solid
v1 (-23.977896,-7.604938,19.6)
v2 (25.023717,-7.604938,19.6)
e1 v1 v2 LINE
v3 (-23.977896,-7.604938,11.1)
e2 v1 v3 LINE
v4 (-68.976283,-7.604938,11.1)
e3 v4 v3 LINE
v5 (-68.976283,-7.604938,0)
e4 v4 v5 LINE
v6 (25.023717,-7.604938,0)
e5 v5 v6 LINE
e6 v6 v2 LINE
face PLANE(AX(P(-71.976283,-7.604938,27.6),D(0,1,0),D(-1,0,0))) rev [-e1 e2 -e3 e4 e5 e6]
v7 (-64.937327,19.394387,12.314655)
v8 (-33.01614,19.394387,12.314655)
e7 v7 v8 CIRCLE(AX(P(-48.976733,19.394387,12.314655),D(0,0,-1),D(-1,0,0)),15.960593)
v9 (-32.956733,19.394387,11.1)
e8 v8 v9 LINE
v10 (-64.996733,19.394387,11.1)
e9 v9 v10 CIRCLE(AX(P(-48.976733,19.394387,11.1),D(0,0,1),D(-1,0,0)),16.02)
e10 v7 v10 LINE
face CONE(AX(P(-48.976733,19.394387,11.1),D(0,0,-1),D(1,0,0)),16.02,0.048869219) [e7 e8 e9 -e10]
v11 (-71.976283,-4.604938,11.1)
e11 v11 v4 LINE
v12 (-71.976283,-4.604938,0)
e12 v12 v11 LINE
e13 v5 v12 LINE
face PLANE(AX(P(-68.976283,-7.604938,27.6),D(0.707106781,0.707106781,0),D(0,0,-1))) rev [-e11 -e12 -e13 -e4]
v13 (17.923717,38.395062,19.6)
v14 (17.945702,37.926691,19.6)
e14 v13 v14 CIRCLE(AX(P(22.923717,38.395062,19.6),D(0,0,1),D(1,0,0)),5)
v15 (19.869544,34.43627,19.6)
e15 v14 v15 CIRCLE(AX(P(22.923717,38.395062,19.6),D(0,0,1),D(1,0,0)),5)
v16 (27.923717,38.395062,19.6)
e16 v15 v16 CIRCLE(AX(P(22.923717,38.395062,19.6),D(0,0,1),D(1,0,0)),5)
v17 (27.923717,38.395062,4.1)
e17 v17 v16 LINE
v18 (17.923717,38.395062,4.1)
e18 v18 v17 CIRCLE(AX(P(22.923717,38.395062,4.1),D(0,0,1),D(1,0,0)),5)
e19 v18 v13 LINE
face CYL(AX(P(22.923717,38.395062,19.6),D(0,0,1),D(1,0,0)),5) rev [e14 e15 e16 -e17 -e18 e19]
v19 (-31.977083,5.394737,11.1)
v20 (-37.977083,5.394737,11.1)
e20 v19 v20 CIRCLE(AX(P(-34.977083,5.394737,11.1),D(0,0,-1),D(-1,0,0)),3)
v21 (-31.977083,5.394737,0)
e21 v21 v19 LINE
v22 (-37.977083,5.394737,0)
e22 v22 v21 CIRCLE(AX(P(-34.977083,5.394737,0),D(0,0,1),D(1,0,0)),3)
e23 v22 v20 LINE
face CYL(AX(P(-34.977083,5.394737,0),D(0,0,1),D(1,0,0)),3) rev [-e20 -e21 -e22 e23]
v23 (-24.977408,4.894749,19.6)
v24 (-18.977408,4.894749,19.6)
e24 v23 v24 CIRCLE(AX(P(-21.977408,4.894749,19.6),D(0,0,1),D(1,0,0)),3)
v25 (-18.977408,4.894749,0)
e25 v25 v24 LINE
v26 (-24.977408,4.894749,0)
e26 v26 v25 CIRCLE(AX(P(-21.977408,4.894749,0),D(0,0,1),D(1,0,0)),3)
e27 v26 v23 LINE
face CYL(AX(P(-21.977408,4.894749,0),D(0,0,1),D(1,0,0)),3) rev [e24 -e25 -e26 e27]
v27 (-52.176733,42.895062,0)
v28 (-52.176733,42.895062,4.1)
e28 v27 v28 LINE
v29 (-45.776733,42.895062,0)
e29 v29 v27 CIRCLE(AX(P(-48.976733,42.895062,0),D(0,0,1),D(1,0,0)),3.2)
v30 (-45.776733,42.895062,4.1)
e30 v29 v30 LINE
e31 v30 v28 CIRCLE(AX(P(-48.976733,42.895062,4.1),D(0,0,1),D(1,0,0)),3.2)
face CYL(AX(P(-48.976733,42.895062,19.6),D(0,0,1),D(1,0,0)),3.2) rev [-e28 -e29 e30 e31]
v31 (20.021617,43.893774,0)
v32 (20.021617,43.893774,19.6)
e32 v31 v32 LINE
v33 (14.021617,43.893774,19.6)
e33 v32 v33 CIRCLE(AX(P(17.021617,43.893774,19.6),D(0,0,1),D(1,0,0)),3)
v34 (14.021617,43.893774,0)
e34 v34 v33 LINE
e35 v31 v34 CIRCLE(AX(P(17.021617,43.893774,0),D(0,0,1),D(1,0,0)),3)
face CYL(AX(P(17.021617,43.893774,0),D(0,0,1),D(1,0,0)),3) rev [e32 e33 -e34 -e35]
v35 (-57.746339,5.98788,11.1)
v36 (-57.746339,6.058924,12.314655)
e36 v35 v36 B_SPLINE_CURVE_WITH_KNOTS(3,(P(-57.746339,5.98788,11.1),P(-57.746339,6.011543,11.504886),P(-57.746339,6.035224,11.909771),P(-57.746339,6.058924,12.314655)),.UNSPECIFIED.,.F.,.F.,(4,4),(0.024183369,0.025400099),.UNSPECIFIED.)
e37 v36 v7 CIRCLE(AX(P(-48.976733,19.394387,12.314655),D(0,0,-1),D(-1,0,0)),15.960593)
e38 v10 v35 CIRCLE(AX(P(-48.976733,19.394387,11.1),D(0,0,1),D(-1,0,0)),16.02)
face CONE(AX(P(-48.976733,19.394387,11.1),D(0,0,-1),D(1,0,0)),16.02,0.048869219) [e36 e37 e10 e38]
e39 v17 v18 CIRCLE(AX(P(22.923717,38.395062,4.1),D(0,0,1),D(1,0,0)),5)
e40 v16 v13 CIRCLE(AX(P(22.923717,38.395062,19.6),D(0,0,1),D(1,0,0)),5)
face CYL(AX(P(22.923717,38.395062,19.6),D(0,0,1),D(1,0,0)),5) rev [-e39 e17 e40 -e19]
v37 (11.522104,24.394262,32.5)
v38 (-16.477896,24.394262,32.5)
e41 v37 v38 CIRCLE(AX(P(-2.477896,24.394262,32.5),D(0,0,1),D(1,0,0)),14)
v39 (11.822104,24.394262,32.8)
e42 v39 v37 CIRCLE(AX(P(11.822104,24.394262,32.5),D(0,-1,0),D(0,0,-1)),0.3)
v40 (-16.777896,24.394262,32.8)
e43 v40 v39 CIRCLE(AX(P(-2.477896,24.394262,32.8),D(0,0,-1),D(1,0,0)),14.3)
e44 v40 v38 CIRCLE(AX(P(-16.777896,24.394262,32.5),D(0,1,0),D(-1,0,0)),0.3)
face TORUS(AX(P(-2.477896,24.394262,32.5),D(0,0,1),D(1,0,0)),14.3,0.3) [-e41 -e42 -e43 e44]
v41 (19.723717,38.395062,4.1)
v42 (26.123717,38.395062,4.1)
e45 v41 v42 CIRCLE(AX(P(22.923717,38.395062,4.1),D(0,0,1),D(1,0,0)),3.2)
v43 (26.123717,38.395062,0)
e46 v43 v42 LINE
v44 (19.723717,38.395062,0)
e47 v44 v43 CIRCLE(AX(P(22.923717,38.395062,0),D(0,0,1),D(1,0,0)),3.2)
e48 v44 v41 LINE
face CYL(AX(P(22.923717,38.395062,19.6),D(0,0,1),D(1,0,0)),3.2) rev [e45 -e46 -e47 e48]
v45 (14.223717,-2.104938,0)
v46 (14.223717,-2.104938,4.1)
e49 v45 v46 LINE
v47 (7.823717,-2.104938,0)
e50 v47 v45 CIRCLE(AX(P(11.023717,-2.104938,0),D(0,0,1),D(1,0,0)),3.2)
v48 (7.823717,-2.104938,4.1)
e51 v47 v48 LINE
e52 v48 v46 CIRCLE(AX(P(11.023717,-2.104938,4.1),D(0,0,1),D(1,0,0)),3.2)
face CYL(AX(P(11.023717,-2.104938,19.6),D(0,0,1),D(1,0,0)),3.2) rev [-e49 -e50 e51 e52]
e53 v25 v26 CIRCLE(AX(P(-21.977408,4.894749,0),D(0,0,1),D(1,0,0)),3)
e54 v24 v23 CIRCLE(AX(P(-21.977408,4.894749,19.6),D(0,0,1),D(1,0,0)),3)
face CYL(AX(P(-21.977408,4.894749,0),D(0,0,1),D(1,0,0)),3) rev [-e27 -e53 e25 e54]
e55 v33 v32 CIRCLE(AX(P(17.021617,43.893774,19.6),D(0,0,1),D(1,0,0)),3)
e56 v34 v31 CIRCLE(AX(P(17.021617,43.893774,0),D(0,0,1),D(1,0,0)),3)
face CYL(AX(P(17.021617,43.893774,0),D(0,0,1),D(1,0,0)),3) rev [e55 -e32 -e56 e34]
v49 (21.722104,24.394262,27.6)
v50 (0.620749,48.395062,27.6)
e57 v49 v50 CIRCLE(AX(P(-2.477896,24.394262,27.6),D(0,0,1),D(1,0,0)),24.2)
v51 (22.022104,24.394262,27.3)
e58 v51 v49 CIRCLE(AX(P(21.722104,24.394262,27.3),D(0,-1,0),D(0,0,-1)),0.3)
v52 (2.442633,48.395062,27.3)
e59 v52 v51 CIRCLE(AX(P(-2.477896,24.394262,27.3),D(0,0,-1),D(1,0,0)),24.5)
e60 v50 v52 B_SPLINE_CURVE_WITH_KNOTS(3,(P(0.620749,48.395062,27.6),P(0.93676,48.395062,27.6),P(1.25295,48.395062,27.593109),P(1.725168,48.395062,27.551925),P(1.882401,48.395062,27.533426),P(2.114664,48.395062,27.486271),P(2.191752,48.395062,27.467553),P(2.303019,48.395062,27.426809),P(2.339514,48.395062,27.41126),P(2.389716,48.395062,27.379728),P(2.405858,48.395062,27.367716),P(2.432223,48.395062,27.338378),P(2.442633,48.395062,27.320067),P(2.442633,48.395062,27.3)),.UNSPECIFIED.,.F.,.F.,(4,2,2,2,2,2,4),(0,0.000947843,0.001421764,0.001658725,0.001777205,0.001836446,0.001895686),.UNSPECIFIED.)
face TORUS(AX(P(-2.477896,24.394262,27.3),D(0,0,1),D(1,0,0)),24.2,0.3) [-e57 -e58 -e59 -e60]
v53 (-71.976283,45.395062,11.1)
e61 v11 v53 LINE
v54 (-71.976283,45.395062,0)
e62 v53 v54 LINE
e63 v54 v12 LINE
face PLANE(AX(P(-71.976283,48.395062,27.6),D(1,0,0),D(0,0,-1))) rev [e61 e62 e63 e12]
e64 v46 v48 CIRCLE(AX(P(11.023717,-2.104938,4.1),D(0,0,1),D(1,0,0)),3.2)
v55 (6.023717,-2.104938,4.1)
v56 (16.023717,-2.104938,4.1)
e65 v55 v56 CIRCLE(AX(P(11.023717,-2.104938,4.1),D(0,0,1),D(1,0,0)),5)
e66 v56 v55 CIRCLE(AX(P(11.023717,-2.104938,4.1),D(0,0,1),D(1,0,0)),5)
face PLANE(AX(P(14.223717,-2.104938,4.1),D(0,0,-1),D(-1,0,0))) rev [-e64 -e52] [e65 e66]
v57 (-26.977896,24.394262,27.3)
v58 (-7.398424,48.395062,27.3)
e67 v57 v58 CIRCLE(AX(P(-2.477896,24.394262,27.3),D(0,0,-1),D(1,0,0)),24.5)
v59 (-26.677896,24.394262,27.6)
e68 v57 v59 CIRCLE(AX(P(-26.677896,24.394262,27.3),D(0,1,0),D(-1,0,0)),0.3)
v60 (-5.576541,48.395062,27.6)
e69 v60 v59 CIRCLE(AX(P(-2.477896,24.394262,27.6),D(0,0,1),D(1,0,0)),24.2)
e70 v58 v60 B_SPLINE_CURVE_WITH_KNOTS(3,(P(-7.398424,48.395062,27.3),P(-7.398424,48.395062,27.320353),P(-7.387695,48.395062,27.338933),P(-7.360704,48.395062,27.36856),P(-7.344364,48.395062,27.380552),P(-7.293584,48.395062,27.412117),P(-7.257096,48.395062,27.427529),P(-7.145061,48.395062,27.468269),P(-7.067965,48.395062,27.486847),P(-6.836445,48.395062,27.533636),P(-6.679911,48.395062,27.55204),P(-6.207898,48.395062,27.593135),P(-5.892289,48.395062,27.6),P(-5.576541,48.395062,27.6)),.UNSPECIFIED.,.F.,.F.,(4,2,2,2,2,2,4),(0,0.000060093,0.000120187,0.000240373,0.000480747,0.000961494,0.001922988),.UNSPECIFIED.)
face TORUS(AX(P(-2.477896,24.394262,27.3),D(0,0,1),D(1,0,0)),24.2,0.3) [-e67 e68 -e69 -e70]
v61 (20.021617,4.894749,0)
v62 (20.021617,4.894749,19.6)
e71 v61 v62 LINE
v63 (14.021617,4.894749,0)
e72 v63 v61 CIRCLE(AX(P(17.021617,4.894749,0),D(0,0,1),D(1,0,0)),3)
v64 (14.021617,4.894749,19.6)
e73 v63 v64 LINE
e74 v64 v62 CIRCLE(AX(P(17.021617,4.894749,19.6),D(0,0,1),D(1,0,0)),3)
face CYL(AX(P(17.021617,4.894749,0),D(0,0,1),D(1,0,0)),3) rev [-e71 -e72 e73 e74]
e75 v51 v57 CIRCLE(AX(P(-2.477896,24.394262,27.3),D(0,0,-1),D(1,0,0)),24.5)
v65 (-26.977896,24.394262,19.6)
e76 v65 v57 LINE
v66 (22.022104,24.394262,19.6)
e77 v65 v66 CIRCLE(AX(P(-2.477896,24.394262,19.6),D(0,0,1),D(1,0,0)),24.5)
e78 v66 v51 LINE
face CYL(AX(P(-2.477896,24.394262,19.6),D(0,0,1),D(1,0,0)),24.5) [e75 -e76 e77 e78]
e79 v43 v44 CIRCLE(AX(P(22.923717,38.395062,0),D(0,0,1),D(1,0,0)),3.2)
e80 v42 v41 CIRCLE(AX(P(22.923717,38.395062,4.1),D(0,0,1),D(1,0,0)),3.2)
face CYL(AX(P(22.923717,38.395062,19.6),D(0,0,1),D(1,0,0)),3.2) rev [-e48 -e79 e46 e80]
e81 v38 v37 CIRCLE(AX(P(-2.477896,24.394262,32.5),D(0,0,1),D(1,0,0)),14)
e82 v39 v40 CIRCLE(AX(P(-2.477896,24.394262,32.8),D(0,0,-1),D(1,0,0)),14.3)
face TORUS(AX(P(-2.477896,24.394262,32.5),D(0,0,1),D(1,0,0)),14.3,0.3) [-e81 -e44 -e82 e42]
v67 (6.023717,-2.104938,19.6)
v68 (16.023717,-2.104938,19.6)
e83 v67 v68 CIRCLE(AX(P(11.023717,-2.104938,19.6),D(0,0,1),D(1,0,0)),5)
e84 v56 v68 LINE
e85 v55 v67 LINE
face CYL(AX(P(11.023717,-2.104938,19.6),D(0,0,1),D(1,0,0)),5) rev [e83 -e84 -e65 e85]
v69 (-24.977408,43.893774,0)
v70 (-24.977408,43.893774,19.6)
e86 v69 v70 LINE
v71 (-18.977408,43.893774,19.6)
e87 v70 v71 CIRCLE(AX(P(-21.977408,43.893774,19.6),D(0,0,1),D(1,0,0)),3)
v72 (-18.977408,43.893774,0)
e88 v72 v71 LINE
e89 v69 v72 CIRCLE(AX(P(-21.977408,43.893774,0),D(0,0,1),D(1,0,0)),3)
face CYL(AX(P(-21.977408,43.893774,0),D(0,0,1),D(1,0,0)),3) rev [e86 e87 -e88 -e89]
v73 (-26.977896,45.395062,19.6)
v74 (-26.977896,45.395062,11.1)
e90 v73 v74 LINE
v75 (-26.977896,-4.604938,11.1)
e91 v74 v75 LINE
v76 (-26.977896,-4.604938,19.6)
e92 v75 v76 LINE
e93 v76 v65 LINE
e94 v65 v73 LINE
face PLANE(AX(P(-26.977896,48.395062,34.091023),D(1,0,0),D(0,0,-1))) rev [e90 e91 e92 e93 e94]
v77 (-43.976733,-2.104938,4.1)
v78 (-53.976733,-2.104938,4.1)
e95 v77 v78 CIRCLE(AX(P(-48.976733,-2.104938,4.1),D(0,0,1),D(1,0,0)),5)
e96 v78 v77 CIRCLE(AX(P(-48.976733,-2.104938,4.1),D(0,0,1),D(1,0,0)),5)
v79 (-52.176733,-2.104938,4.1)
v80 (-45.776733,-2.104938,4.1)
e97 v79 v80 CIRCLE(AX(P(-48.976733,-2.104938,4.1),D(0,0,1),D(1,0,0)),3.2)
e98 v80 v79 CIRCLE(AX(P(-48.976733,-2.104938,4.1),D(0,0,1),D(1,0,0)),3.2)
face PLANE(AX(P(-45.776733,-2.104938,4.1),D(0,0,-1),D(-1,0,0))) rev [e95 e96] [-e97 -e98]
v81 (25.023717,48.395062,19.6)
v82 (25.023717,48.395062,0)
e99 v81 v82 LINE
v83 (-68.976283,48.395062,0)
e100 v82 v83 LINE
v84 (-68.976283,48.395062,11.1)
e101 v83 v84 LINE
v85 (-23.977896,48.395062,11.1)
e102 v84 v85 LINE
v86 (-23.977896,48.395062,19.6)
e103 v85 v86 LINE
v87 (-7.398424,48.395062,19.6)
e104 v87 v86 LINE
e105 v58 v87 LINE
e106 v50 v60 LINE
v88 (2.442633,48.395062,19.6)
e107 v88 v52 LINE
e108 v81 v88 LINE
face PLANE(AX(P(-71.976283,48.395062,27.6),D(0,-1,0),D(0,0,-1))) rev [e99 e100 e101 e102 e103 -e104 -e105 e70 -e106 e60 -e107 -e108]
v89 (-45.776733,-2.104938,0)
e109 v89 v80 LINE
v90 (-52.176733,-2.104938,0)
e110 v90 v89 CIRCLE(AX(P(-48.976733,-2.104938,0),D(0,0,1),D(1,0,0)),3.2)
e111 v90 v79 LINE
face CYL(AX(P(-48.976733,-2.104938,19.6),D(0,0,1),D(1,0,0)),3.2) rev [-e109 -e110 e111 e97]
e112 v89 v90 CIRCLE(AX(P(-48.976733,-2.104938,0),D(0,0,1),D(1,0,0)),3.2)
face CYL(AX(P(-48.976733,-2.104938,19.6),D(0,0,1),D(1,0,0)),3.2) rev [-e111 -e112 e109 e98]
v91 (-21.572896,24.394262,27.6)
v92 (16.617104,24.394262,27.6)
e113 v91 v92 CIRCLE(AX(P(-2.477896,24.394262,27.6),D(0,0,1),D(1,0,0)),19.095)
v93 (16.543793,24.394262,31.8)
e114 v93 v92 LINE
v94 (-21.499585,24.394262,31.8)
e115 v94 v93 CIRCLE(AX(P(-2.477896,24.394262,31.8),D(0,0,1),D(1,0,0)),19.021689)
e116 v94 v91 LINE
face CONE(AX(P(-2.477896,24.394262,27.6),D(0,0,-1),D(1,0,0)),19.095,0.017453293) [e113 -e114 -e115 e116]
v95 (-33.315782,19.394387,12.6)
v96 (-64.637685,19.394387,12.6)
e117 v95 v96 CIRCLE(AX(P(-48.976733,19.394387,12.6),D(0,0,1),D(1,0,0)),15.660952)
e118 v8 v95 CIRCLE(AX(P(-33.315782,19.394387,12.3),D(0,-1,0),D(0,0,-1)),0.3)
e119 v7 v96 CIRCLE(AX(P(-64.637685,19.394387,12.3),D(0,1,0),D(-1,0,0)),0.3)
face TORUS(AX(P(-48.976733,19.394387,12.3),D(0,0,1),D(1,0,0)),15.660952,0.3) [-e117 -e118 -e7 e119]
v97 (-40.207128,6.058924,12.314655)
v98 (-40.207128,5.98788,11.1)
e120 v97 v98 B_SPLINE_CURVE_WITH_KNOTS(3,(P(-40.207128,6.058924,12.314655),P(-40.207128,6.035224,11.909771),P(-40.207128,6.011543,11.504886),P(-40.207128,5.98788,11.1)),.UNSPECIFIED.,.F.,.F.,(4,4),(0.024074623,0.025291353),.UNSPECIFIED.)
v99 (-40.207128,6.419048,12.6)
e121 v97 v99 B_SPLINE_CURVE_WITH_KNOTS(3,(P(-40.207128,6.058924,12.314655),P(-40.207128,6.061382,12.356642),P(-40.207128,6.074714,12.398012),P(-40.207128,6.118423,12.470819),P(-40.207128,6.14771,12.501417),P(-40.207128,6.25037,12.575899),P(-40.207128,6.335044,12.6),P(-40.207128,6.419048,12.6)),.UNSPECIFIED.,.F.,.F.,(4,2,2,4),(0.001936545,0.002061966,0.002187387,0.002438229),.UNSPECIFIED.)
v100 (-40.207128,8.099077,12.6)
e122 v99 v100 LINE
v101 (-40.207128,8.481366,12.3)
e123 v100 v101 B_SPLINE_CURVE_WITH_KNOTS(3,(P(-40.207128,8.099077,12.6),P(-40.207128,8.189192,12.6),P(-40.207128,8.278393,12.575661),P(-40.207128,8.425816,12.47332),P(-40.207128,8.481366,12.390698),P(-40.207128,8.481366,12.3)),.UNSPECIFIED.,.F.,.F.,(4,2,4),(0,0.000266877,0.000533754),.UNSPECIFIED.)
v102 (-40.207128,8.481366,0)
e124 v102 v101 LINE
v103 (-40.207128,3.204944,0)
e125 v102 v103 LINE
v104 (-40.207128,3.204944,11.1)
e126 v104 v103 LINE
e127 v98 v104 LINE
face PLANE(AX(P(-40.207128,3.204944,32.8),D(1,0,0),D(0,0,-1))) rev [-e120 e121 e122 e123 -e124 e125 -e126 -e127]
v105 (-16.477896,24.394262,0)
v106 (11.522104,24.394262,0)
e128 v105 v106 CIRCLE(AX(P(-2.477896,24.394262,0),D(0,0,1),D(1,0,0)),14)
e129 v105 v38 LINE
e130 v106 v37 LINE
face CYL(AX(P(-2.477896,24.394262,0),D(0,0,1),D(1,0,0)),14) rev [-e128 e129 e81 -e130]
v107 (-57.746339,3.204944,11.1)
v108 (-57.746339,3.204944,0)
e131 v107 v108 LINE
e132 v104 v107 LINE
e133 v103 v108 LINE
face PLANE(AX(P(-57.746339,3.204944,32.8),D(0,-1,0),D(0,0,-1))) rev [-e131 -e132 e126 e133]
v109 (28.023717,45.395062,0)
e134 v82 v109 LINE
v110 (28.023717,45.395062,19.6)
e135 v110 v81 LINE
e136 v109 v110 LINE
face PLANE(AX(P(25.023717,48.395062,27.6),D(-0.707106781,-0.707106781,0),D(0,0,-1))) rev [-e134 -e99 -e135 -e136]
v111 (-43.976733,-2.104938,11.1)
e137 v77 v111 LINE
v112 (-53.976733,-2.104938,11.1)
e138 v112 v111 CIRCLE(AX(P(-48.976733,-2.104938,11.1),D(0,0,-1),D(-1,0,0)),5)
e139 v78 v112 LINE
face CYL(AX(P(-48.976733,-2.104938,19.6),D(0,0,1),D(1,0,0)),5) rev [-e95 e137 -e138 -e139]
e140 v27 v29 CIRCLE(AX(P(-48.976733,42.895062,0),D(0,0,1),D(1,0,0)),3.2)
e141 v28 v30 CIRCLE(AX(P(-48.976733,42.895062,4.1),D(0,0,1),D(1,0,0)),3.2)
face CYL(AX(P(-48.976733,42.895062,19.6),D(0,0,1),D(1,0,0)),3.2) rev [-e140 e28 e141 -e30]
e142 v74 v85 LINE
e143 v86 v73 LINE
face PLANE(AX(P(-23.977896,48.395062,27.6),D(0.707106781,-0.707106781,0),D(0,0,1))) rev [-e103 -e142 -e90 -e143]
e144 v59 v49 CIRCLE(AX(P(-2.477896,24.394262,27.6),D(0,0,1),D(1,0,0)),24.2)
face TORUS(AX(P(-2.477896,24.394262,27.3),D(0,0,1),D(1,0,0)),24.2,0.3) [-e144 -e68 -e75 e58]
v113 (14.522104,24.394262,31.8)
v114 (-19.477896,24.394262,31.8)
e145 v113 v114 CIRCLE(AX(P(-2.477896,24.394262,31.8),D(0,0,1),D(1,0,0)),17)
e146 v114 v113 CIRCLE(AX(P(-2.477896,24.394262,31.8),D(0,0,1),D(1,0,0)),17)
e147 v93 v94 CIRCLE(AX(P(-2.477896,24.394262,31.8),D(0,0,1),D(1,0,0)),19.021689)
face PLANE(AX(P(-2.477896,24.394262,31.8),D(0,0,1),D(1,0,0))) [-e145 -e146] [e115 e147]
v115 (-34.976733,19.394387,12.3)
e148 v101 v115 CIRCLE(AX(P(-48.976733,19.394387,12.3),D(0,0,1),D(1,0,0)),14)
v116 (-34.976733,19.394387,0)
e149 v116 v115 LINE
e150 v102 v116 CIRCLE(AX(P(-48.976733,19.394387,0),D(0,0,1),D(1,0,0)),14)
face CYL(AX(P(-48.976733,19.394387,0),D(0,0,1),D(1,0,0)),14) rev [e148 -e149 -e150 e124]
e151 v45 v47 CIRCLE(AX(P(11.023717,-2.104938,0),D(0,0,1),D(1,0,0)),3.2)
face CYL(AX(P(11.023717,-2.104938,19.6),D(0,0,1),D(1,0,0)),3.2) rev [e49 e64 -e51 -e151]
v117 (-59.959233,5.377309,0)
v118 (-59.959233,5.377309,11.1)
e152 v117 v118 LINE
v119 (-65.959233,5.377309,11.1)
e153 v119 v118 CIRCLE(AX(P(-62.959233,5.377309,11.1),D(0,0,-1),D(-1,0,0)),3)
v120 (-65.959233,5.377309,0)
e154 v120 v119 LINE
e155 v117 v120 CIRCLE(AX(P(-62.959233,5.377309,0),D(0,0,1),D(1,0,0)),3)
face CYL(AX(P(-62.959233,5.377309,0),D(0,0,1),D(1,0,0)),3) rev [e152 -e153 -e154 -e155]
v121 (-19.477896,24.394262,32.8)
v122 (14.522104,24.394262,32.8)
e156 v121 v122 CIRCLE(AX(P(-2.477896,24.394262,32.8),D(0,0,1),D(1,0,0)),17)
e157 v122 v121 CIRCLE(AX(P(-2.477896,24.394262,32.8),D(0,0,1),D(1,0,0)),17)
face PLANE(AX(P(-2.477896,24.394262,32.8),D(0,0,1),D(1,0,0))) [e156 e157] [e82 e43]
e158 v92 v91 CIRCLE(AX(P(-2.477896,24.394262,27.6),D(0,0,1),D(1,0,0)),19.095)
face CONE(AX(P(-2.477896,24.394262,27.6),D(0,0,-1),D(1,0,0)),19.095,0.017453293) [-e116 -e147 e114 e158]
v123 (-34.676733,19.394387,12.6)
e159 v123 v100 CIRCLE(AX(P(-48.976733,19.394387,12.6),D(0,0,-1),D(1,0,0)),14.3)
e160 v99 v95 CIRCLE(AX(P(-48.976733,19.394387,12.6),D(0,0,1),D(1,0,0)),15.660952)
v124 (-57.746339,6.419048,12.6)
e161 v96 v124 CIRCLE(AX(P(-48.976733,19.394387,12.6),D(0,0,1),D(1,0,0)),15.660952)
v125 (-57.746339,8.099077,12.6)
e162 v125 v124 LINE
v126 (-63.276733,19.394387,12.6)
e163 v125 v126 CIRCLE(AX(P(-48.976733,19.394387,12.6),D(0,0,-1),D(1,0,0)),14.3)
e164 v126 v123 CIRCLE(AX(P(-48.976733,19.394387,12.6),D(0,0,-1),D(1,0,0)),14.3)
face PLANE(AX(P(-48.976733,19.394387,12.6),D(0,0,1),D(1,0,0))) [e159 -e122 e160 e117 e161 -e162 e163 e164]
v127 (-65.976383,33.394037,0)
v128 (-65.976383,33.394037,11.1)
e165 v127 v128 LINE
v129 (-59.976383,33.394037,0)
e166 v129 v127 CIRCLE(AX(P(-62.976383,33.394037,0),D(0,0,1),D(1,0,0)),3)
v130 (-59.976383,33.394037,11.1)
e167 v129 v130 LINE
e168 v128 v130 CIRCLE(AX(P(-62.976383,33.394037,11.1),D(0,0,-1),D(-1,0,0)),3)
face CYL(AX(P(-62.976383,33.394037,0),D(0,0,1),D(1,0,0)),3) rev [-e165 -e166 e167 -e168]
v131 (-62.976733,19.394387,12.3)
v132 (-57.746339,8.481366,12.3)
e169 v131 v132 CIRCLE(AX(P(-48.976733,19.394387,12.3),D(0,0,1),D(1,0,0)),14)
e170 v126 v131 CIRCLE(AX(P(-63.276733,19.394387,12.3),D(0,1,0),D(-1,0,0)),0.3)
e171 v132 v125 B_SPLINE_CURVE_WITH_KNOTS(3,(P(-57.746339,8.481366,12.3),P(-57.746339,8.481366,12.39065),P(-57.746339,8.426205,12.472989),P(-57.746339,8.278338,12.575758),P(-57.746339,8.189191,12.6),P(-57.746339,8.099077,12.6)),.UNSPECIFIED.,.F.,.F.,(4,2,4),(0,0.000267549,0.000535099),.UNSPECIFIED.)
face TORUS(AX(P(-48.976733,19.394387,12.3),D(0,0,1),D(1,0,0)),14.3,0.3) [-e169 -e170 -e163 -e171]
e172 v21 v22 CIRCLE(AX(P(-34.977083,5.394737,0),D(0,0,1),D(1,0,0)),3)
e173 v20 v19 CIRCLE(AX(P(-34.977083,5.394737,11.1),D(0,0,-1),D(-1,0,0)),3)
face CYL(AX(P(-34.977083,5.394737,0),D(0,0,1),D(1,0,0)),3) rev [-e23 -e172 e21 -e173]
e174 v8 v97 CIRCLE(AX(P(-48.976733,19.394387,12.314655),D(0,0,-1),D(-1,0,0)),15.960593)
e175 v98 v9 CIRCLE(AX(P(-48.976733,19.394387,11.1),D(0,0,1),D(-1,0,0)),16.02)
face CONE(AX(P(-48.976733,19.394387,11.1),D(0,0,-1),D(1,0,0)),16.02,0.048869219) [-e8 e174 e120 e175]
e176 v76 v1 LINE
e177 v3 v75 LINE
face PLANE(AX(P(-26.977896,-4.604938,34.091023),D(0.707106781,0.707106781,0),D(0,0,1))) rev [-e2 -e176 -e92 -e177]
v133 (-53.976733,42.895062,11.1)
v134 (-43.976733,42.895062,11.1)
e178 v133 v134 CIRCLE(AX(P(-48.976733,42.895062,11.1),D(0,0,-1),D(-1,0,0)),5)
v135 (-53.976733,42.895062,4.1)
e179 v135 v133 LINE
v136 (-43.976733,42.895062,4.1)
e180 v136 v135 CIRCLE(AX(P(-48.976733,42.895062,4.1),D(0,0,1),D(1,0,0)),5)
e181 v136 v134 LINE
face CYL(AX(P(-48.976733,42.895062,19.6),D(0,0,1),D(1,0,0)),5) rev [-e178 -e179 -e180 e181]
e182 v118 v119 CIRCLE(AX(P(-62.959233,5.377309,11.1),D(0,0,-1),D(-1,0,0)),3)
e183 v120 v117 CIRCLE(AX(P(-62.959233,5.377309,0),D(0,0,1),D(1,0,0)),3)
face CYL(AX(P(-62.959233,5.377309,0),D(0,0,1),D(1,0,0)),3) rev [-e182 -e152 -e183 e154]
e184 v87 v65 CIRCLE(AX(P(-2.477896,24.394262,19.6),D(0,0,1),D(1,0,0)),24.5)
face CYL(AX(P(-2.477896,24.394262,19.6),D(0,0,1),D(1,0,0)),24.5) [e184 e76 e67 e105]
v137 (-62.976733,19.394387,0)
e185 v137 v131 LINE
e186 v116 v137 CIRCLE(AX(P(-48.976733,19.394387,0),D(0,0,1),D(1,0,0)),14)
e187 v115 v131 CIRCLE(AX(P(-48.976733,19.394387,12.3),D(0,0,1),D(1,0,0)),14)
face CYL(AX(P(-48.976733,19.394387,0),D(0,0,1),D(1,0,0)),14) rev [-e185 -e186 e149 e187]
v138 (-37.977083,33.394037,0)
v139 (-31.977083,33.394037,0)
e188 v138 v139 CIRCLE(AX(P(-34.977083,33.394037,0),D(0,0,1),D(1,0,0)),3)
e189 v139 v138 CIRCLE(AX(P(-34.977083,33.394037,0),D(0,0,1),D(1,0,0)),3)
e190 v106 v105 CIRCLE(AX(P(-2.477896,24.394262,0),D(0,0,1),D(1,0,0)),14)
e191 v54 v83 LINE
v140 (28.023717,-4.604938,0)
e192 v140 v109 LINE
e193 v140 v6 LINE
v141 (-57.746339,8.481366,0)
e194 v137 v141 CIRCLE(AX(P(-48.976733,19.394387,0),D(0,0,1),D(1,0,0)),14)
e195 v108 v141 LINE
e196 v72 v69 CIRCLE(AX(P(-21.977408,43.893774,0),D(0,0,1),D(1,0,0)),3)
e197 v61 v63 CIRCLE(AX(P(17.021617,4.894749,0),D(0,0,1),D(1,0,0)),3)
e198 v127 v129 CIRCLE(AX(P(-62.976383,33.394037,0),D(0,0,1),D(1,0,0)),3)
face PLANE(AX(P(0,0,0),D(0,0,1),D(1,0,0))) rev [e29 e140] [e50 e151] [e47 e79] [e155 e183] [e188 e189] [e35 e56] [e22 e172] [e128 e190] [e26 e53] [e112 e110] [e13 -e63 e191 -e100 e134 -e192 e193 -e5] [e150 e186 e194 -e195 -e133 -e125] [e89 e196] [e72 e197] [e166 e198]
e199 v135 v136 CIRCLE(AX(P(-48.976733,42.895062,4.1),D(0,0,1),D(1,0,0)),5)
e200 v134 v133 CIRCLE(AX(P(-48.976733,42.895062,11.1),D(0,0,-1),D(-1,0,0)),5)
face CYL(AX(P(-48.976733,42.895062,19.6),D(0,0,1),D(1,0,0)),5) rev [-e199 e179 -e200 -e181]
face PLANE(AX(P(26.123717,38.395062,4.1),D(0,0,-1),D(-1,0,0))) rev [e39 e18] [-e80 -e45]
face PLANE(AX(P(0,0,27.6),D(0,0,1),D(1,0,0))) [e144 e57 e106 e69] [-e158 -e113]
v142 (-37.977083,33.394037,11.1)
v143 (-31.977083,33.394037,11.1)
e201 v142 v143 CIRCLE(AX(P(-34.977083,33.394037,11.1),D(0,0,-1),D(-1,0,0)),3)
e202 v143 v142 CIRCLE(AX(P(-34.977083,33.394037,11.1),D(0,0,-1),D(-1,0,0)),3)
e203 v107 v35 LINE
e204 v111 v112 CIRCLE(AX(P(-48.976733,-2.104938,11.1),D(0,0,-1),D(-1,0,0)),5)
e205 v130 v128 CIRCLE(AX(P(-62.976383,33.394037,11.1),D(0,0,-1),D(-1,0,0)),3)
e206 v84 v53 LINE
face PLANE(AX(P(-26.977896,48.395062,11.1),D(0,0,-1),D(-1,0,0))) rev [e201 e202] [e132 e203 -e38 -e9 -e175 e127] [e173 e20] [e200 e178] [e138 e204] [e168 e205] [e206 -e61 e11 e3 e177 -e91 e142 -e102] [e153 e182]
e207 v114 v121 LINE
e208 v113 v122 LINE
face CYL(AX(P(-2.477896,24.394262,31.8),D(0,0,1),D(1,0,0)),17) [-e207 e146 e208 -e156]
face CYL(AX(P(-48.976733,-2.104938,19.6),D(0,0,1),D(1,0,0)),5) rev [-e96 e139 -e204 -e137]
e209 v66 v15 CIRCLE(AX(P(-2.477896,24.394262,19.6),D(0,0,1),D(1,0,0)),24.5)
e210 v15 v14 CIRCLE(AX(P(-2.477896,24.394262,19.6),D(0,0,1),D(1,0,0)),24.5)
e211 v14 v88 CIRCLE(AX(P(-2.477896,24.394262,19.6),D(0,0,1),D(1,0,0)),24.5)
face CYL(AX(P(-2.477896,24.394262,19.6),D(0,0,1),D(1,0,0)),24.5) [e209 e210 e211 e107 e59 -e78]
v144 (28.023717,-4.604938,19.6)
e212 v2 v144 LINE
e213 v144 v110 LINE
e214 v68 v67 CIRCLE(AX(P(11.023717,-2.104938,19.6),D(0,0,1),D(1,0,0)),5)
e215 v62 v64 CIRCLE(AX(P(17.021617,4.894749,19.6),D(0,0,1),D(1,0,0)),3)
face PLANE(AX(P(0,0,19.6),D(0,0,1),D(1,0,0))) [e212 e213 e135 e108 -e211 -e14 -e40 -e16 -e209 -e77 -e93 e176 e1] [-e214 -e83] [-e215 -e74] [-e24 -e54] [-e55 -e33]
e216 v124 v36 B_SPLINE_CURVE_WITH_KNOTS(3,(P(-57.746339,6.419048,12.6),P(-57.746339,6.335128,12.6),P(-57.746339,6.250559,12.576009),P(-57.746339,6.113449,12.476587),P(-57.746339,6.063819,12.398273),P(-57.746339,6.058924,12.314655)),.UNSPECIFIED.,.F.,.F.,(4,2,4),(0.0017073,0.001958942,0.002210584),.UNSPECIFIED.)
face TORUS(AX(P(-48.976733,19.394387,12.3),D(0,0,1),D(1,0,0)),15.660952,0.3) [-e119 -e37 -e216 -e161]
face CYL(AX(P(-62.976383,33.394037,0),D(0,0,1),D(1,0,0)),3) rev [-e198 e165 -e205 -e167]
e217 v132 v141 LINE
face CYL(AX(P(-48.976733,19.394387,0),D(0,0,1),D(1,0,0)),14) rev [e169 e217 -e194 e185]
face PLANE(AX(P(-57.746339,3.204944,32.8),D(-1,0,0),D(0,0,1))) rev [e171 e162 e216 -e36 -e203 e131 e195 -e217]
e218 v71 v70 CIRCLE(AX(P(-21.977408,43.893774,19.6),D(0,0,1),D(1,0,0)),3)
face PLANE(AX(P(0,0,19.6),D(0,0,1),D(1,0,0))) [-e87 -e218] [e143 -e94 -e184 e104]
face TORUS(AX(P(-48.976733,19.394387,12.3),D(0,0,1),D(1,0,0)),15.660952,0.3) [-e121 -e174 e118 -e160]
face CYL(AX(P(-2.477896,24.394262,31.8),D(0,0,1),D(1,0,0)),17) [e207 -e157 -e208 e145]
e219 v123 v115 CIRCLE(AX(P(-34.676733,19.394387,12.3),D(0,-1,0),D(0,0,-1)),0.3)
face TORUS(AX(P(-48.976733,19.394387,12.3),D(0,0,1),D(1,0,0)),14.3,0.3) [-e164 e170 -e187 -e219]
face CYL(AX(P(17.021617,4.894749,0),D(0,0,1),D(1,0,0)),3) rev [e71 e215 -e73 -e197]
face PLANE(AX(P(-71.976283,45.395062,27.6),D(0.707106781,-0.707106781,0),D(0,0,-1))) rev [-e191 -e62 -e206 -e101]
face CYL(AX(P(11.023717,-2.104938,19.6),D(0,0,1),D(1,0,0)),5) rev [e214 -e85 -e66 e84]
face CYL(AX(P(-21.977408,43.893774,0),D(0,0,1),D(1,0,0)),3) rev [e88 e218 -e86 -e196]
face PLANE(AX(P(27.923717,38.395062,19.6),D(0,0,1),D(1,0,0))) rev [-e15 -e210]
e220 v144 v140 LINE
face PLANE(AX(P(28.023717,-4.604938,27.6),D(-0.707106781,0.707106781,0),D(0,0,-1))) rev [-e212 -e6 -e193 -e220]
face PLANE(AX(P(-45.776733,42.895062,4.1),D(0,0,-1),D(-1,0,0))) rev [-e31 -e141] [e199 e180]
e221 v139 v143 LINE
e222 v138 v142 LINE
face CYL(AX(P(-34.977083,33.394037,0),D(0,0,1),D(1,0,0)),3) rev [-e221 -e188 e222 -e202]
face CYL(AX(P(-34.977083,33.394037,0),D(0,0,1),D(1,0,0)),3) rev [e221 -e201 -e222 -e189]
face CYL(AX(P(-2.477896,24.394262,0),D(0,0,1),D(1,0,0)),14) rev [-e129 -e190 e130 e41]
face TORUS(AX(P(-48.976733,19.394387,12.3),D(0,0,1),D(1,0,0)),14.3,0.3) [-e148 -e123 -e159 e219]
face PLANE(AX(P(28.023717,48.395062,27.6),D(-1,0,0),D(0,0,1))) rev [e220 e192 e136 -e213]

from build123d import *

# Parameters (mm, degrees)
SKETCH1_W                                    = 100
SKETCH1_H                                    = 56
BOSS_EXTRUDE1_DEPTH                          = 27.6
SKETCH2_R                                    = 19.095
BOSS_EXTRUDE2_DEPTH                          = 5.2
BOSS_EXTRUDE2_TAPER                          = 1
SKETCH4_W                                    = 117.356631531
SKETCH4_H                                    = 93.478875332
SKETCH4_R                                    = 24.5
CUT_EXTRUDE1_DEPTH                           = 8
FILLET1_R                                    = 0.3
SKETCH5_W                                    = 56.36290192
SKETCH5_H                                    = 22.991022885
CUT_EXTRUDE2_DEPTH                           = 97.914526075
SKETCH6_R                                    = 16.02
BOSS_EXTRUDE3_DEPTH                          = 1.5
BOSS_EXTRUDE3_TAPER                          = 2.8
FILLET2_R                                    = 0.3
CUT_EXTRUDE3_DEPTH                           = 90.406696404
CUT_EXTRUDE3_DEPTH_BACK                      = 90.406696404
SKETCH7_R                                    = 3
SKETCH8_R                                    = 14
CUT_EXTRUDE4_DEPTH                           = 90.054519041
SKETCH9_W                                    = 17.539210826
SKETCH9_H                                    = 13.762480841
CUT_EXTRUDE5_DEPTH                           = 93.728136852
CHAMFER1_SIZE                                = 3
CBORE_FOR_M6_HEX_SOCKET_HEAD_CAP_SCR_2_COUNT = 2
CBORE_FOR_M6_HEX_SOCKET_HEAD_CAP_SCR_2_PITCH = 75.00036
CBORE_FOR_M6_HEX_SOCKET_HEAD_CAP_SCR_3_COUNT = 2
CBORE_FOR_M6_HEX_SOCKET_HEAD_CAP_SCR_3_PITCH = 45
CBORE_FOR_M6_HEX_SOCKET_HEAD_CAP_SCR_4_COUNT = 2
CBORE_FOR_M6_HEX_SOCKET_HEAD_CAP_SCR_4_PITCH = 72.041132072
SKETCH12_R                                   = 14
CUT_EXTRUDE6_DEPTH                           = 93.728136852
FILLET3_R                                    = 0.3
SKETCH13_R                                   = 21.226121865
SKETCH13_R_2                                 = 17
CUT_EXTRUDE7_DEPTH                           = 1


with BuildPart() as part:
    # Sketch1 → Boss-Extrude1 (new body)
    with BuildSketch(Plane.XY):
        with Locations((-21.976283301, 20.395061728)):
            Rectangle(SKETCH1_W, SKETCH1_H)
    extrude(amount=BOSS_EXTRUDE1_DEPTH)

    # Sketch2 → Boss-Extrude2 (add)
    with BuildSketch(Plane.XY.offset(27.6)):
        with Locations((-2.477895801, 24.394261729)):
            Circle(SKETCH2_R)
    extrude(amount=BOSS_EXTRUDE2_DEPTH, taper=BOSS_EXTRUDE2_TAPER)

    # Sketch4 → Cut-Extrude1 (cut)
    with BuildSketch(Plane.XY.offset(27.6)):
        with Locations((-19.266750683, 19.548332785)):
            Rectangle(SKETCH4_W, SKETCH4_H)
        with Locations((-2.477895801, 24.394261729)):
            Circle(SKETCH4_R, mode=Mode.SUBTRACT)
    extrude(amount=-CUT_EXTRUDE1_DEPTH, mode=Mode.SUBTRACT)

    # Fillet1
    fillet1_edges = [part.edges().sort_by_distance(p)[0] for p in [
        (-21.482129463, 24.394261729, 32.8),
    ]]
    fillet(fillet1_edges, radius=FILLET1_R)

    # Sketch5 → Cut-Extrude2 (cut, through all)
    with BuildSketch(Plane.XZ.offset(7.604938272)):
        with Locations((-55.159346761, 22.595511443)):
            Rectangle(SKETCH5_W, SKETCH5_H)
    extrude(amount=-CUT_EXTRUDE2_DEPTH, mode=Mode.SUBTRACT)

    # Sketch6 → Boss-Extrude3 (add)
    with BuildSketch(Plane.XY.offset(11.1)):
        with Locations((-48.976733301, 19.394386728)):
            Circle(SKETCH6_R)
    extrude(amount=BOSS_EXTRUDE3_DEPTH, taper=BOSS_EXTRUDE3_TAPER)

    # Fillet2
    fillet2_edges = [part.edges().sort_by_distance(p)[0] for p in [
        (-64.923371062, 19.394386728, 12.6),
    ]]
    fillet(fillet2_edges, radius=FILLET2_R)

    # Sketch7 → Cut-Extrude3 (cut, two sides: drawn at the far end of the back side and taken through both)
    with BuildSketch(Plane.XY.offset(11.1).offset(-CUT_EXTRUDE3_DEPTH_BACK)):
        with Locations((-62.976383301, 33.394036728)):
            Circle(SKETCH7_R)
        with Locations((-34.977083301, 5.394736728)):
            Circle(SKETCH7_R)
        with Locations((-62.959232869, 5.377309322)):
            Circle(SKETCH7_R)
        with Locations((-34.977083301, 33.394036728)):
            Circle(SKETCH7_R)
        with Locations((-21.977408301, 4.894749229)):
            Circle(SKETCH7_R)
        with Locations((17.021616699, 4.894749228)):
            Circle(SKETCH7_R)
        with Locations((-21.977408301, 43.893774228)):
            Circle(SKETCH7_R)
        with Locations((17.021616699, 43.893774228)):
            Circle(SKETCH7_R)
    extrude(amount=CUT_EXTRUDE3_DEPTH + CUT_EXTRUDE3_DEPTH_BACK, mode=Mode.SUBTRACT)

    # Sketch8 → Cut-Extrude4 (cut, through all)
    with BuildSketch(Plane.XY.offset(12.6)):
        with Locations((-48.976733301, 19.394386728)):
            Circle(SKETCH8_R)
    extrude(amount=-CUT_EXTRUDE4_DEPTH, mode=Mode.SUBTRACT)

    # Sketch9 → Cut-Extrude5 (cut, through all)
    with BuildSketch(Plane(origin=(0, 0, 0), x_dir=(-1, 0, 0), z_dir=(0, 0, -1))):
        with Locations((48.976733301, 10.086184236)):
            Rectangle(SKETCH9_W, SKETCH9_H)
    extrude(amount=-CUT_EXTRUDE5_DEPTH, mode=Mode.SUBTRACT)

    # Chamfer1
    chamfer1_edges = [part.edges().sort_by_distance(p)[0] for p in [
        (28.023716699, 48.395061728, 9.8),
        (28.023716699, -7.604938272, 9.8),
        (-71.976283301, 48.395061728, 5.55),
        (-71.976283301, -7.604938272, 5.55),
        (-26.977895801, -7.604938272, 15.35),
        (-26.977895801, 48.395061728, 15.35),
    ]]
    chamfer(chamfer1_edges, length=CHAMFER1_SIZE)

    # Sketch11 → CBORE for M6 Hex Socket Head Cap Screw1 (revolve, cut)
    with BuildSketch(Plane(origin=(-48.976733301, 42.895061728, 19.6), x_dir=(0, -1, 0), z_dir=(1, 0, 0))):
        Polygon((0, 0), (0, 19.6), (3.2, 19.6), (3.2, 15.5), (5, 15.5), (5, 0), align=None)
    cbore_for_m6_hex_socket_head_cap_screw1 = revolve(axis=Axis((-48.976733301, 42.895061728, 25.95), (0, 0, -1)), mode=Mode.SUBTRACT)

    # CBORE for M6 Hex Socket Head Cap Scr 2: CBORE for M6 Hex Socket Head Cap Screw1 ×2
    with Locations(*[Vector(0.8000021599844496, -0.5999971200099341, 0) * (i * CBORE_FOR_M6_HEX_SOCKET_HEAD_CAP_SCR_2_PITCH) for i in range(1, CBORE_FOR_M6_HEX_SOCKET_HEAD_CAP_SCR_2_COUNT)]):
        add(cbore_for_m6_hex_socket_head_cap_screw1, mode=Mode.SUBTRACT)

    # CBORE for M6 Hex Socket Head Cap Scr 3: CBORE for M6 Hex Socket Head Cap Screw1 ×2
    with Locations(*[(0, -i * CBORE_FOR_M6_HEX_SOCKET_HEAD_CAP_SCR_3_PITCH, 0) for i in range(1, CBORE_FOR_M6_HEX_SOCKET_HEAD_CAP_SCR_3_COUNT)]):
        add(cbore_for_m6_hex_socket_head_cap_screw1, mode=Mode.SUBTRACT)

    # CBORE for M6 Hex Socket Head Cap Scr 4: CBORE for M6 Hex Socket Head Cap Screw1 ×2
    with Locations(*[Vector(0.9980471979289498, -0.06246431546228526, 0) * (i * CBORE_FOR_M6_HEX_SOCKET_HEAD_CAP_SCR_4_PITCH) for i in range(1, CBORE_FOR_M6_HEX_SOCKET_HEAD_CAP_SCR_4_COUNT)]):
        add(cbore_for_m6_hex_socket_head_cap_screw1, mode=Mode.SUBTRACT)

    # Sketch12 → Cut-Extrude6 (cut, through all)
    with BuildSketch(Plane.XY.offset(32.8)):
        with Locations((-2.477895801, 24.394261729)):
            Circle(SKETCH12_R)
    extrude(amount=-CUT_EXTRUDE6_DEPTH, mode=Mode.SUBTRACT)

    # Fillet3
    fillet3_edges = [part.edges().sort_by_distance(p)[0] for p in [
        (-48.976733301, 33.394386728, 12.6),
        (-2.477895801, -0.105738271, 27.6),
        (-16.477895801, 24.394261729, 32.8),
    ]]
    fillet(fillet3_edges, radius=FILLET3_R)

    # Sketch13 → Cut-Extrude7 (cut)
    with BuildSketch(Plane.XY.offset(32.8)):
        with Locations((-2.477895801, 24.394261729)):
            Circle(SKETCH13_R)
        with Locations((-2.477895801, 24.394261729)):
            Circle(SKETCH13_R_2, mode=Mode.SUBTRACT)
    extrude(amount=-CUT_EXTRUDE7_DEPTH, mode=Mode.SUBTRACT)


solid = part.part
